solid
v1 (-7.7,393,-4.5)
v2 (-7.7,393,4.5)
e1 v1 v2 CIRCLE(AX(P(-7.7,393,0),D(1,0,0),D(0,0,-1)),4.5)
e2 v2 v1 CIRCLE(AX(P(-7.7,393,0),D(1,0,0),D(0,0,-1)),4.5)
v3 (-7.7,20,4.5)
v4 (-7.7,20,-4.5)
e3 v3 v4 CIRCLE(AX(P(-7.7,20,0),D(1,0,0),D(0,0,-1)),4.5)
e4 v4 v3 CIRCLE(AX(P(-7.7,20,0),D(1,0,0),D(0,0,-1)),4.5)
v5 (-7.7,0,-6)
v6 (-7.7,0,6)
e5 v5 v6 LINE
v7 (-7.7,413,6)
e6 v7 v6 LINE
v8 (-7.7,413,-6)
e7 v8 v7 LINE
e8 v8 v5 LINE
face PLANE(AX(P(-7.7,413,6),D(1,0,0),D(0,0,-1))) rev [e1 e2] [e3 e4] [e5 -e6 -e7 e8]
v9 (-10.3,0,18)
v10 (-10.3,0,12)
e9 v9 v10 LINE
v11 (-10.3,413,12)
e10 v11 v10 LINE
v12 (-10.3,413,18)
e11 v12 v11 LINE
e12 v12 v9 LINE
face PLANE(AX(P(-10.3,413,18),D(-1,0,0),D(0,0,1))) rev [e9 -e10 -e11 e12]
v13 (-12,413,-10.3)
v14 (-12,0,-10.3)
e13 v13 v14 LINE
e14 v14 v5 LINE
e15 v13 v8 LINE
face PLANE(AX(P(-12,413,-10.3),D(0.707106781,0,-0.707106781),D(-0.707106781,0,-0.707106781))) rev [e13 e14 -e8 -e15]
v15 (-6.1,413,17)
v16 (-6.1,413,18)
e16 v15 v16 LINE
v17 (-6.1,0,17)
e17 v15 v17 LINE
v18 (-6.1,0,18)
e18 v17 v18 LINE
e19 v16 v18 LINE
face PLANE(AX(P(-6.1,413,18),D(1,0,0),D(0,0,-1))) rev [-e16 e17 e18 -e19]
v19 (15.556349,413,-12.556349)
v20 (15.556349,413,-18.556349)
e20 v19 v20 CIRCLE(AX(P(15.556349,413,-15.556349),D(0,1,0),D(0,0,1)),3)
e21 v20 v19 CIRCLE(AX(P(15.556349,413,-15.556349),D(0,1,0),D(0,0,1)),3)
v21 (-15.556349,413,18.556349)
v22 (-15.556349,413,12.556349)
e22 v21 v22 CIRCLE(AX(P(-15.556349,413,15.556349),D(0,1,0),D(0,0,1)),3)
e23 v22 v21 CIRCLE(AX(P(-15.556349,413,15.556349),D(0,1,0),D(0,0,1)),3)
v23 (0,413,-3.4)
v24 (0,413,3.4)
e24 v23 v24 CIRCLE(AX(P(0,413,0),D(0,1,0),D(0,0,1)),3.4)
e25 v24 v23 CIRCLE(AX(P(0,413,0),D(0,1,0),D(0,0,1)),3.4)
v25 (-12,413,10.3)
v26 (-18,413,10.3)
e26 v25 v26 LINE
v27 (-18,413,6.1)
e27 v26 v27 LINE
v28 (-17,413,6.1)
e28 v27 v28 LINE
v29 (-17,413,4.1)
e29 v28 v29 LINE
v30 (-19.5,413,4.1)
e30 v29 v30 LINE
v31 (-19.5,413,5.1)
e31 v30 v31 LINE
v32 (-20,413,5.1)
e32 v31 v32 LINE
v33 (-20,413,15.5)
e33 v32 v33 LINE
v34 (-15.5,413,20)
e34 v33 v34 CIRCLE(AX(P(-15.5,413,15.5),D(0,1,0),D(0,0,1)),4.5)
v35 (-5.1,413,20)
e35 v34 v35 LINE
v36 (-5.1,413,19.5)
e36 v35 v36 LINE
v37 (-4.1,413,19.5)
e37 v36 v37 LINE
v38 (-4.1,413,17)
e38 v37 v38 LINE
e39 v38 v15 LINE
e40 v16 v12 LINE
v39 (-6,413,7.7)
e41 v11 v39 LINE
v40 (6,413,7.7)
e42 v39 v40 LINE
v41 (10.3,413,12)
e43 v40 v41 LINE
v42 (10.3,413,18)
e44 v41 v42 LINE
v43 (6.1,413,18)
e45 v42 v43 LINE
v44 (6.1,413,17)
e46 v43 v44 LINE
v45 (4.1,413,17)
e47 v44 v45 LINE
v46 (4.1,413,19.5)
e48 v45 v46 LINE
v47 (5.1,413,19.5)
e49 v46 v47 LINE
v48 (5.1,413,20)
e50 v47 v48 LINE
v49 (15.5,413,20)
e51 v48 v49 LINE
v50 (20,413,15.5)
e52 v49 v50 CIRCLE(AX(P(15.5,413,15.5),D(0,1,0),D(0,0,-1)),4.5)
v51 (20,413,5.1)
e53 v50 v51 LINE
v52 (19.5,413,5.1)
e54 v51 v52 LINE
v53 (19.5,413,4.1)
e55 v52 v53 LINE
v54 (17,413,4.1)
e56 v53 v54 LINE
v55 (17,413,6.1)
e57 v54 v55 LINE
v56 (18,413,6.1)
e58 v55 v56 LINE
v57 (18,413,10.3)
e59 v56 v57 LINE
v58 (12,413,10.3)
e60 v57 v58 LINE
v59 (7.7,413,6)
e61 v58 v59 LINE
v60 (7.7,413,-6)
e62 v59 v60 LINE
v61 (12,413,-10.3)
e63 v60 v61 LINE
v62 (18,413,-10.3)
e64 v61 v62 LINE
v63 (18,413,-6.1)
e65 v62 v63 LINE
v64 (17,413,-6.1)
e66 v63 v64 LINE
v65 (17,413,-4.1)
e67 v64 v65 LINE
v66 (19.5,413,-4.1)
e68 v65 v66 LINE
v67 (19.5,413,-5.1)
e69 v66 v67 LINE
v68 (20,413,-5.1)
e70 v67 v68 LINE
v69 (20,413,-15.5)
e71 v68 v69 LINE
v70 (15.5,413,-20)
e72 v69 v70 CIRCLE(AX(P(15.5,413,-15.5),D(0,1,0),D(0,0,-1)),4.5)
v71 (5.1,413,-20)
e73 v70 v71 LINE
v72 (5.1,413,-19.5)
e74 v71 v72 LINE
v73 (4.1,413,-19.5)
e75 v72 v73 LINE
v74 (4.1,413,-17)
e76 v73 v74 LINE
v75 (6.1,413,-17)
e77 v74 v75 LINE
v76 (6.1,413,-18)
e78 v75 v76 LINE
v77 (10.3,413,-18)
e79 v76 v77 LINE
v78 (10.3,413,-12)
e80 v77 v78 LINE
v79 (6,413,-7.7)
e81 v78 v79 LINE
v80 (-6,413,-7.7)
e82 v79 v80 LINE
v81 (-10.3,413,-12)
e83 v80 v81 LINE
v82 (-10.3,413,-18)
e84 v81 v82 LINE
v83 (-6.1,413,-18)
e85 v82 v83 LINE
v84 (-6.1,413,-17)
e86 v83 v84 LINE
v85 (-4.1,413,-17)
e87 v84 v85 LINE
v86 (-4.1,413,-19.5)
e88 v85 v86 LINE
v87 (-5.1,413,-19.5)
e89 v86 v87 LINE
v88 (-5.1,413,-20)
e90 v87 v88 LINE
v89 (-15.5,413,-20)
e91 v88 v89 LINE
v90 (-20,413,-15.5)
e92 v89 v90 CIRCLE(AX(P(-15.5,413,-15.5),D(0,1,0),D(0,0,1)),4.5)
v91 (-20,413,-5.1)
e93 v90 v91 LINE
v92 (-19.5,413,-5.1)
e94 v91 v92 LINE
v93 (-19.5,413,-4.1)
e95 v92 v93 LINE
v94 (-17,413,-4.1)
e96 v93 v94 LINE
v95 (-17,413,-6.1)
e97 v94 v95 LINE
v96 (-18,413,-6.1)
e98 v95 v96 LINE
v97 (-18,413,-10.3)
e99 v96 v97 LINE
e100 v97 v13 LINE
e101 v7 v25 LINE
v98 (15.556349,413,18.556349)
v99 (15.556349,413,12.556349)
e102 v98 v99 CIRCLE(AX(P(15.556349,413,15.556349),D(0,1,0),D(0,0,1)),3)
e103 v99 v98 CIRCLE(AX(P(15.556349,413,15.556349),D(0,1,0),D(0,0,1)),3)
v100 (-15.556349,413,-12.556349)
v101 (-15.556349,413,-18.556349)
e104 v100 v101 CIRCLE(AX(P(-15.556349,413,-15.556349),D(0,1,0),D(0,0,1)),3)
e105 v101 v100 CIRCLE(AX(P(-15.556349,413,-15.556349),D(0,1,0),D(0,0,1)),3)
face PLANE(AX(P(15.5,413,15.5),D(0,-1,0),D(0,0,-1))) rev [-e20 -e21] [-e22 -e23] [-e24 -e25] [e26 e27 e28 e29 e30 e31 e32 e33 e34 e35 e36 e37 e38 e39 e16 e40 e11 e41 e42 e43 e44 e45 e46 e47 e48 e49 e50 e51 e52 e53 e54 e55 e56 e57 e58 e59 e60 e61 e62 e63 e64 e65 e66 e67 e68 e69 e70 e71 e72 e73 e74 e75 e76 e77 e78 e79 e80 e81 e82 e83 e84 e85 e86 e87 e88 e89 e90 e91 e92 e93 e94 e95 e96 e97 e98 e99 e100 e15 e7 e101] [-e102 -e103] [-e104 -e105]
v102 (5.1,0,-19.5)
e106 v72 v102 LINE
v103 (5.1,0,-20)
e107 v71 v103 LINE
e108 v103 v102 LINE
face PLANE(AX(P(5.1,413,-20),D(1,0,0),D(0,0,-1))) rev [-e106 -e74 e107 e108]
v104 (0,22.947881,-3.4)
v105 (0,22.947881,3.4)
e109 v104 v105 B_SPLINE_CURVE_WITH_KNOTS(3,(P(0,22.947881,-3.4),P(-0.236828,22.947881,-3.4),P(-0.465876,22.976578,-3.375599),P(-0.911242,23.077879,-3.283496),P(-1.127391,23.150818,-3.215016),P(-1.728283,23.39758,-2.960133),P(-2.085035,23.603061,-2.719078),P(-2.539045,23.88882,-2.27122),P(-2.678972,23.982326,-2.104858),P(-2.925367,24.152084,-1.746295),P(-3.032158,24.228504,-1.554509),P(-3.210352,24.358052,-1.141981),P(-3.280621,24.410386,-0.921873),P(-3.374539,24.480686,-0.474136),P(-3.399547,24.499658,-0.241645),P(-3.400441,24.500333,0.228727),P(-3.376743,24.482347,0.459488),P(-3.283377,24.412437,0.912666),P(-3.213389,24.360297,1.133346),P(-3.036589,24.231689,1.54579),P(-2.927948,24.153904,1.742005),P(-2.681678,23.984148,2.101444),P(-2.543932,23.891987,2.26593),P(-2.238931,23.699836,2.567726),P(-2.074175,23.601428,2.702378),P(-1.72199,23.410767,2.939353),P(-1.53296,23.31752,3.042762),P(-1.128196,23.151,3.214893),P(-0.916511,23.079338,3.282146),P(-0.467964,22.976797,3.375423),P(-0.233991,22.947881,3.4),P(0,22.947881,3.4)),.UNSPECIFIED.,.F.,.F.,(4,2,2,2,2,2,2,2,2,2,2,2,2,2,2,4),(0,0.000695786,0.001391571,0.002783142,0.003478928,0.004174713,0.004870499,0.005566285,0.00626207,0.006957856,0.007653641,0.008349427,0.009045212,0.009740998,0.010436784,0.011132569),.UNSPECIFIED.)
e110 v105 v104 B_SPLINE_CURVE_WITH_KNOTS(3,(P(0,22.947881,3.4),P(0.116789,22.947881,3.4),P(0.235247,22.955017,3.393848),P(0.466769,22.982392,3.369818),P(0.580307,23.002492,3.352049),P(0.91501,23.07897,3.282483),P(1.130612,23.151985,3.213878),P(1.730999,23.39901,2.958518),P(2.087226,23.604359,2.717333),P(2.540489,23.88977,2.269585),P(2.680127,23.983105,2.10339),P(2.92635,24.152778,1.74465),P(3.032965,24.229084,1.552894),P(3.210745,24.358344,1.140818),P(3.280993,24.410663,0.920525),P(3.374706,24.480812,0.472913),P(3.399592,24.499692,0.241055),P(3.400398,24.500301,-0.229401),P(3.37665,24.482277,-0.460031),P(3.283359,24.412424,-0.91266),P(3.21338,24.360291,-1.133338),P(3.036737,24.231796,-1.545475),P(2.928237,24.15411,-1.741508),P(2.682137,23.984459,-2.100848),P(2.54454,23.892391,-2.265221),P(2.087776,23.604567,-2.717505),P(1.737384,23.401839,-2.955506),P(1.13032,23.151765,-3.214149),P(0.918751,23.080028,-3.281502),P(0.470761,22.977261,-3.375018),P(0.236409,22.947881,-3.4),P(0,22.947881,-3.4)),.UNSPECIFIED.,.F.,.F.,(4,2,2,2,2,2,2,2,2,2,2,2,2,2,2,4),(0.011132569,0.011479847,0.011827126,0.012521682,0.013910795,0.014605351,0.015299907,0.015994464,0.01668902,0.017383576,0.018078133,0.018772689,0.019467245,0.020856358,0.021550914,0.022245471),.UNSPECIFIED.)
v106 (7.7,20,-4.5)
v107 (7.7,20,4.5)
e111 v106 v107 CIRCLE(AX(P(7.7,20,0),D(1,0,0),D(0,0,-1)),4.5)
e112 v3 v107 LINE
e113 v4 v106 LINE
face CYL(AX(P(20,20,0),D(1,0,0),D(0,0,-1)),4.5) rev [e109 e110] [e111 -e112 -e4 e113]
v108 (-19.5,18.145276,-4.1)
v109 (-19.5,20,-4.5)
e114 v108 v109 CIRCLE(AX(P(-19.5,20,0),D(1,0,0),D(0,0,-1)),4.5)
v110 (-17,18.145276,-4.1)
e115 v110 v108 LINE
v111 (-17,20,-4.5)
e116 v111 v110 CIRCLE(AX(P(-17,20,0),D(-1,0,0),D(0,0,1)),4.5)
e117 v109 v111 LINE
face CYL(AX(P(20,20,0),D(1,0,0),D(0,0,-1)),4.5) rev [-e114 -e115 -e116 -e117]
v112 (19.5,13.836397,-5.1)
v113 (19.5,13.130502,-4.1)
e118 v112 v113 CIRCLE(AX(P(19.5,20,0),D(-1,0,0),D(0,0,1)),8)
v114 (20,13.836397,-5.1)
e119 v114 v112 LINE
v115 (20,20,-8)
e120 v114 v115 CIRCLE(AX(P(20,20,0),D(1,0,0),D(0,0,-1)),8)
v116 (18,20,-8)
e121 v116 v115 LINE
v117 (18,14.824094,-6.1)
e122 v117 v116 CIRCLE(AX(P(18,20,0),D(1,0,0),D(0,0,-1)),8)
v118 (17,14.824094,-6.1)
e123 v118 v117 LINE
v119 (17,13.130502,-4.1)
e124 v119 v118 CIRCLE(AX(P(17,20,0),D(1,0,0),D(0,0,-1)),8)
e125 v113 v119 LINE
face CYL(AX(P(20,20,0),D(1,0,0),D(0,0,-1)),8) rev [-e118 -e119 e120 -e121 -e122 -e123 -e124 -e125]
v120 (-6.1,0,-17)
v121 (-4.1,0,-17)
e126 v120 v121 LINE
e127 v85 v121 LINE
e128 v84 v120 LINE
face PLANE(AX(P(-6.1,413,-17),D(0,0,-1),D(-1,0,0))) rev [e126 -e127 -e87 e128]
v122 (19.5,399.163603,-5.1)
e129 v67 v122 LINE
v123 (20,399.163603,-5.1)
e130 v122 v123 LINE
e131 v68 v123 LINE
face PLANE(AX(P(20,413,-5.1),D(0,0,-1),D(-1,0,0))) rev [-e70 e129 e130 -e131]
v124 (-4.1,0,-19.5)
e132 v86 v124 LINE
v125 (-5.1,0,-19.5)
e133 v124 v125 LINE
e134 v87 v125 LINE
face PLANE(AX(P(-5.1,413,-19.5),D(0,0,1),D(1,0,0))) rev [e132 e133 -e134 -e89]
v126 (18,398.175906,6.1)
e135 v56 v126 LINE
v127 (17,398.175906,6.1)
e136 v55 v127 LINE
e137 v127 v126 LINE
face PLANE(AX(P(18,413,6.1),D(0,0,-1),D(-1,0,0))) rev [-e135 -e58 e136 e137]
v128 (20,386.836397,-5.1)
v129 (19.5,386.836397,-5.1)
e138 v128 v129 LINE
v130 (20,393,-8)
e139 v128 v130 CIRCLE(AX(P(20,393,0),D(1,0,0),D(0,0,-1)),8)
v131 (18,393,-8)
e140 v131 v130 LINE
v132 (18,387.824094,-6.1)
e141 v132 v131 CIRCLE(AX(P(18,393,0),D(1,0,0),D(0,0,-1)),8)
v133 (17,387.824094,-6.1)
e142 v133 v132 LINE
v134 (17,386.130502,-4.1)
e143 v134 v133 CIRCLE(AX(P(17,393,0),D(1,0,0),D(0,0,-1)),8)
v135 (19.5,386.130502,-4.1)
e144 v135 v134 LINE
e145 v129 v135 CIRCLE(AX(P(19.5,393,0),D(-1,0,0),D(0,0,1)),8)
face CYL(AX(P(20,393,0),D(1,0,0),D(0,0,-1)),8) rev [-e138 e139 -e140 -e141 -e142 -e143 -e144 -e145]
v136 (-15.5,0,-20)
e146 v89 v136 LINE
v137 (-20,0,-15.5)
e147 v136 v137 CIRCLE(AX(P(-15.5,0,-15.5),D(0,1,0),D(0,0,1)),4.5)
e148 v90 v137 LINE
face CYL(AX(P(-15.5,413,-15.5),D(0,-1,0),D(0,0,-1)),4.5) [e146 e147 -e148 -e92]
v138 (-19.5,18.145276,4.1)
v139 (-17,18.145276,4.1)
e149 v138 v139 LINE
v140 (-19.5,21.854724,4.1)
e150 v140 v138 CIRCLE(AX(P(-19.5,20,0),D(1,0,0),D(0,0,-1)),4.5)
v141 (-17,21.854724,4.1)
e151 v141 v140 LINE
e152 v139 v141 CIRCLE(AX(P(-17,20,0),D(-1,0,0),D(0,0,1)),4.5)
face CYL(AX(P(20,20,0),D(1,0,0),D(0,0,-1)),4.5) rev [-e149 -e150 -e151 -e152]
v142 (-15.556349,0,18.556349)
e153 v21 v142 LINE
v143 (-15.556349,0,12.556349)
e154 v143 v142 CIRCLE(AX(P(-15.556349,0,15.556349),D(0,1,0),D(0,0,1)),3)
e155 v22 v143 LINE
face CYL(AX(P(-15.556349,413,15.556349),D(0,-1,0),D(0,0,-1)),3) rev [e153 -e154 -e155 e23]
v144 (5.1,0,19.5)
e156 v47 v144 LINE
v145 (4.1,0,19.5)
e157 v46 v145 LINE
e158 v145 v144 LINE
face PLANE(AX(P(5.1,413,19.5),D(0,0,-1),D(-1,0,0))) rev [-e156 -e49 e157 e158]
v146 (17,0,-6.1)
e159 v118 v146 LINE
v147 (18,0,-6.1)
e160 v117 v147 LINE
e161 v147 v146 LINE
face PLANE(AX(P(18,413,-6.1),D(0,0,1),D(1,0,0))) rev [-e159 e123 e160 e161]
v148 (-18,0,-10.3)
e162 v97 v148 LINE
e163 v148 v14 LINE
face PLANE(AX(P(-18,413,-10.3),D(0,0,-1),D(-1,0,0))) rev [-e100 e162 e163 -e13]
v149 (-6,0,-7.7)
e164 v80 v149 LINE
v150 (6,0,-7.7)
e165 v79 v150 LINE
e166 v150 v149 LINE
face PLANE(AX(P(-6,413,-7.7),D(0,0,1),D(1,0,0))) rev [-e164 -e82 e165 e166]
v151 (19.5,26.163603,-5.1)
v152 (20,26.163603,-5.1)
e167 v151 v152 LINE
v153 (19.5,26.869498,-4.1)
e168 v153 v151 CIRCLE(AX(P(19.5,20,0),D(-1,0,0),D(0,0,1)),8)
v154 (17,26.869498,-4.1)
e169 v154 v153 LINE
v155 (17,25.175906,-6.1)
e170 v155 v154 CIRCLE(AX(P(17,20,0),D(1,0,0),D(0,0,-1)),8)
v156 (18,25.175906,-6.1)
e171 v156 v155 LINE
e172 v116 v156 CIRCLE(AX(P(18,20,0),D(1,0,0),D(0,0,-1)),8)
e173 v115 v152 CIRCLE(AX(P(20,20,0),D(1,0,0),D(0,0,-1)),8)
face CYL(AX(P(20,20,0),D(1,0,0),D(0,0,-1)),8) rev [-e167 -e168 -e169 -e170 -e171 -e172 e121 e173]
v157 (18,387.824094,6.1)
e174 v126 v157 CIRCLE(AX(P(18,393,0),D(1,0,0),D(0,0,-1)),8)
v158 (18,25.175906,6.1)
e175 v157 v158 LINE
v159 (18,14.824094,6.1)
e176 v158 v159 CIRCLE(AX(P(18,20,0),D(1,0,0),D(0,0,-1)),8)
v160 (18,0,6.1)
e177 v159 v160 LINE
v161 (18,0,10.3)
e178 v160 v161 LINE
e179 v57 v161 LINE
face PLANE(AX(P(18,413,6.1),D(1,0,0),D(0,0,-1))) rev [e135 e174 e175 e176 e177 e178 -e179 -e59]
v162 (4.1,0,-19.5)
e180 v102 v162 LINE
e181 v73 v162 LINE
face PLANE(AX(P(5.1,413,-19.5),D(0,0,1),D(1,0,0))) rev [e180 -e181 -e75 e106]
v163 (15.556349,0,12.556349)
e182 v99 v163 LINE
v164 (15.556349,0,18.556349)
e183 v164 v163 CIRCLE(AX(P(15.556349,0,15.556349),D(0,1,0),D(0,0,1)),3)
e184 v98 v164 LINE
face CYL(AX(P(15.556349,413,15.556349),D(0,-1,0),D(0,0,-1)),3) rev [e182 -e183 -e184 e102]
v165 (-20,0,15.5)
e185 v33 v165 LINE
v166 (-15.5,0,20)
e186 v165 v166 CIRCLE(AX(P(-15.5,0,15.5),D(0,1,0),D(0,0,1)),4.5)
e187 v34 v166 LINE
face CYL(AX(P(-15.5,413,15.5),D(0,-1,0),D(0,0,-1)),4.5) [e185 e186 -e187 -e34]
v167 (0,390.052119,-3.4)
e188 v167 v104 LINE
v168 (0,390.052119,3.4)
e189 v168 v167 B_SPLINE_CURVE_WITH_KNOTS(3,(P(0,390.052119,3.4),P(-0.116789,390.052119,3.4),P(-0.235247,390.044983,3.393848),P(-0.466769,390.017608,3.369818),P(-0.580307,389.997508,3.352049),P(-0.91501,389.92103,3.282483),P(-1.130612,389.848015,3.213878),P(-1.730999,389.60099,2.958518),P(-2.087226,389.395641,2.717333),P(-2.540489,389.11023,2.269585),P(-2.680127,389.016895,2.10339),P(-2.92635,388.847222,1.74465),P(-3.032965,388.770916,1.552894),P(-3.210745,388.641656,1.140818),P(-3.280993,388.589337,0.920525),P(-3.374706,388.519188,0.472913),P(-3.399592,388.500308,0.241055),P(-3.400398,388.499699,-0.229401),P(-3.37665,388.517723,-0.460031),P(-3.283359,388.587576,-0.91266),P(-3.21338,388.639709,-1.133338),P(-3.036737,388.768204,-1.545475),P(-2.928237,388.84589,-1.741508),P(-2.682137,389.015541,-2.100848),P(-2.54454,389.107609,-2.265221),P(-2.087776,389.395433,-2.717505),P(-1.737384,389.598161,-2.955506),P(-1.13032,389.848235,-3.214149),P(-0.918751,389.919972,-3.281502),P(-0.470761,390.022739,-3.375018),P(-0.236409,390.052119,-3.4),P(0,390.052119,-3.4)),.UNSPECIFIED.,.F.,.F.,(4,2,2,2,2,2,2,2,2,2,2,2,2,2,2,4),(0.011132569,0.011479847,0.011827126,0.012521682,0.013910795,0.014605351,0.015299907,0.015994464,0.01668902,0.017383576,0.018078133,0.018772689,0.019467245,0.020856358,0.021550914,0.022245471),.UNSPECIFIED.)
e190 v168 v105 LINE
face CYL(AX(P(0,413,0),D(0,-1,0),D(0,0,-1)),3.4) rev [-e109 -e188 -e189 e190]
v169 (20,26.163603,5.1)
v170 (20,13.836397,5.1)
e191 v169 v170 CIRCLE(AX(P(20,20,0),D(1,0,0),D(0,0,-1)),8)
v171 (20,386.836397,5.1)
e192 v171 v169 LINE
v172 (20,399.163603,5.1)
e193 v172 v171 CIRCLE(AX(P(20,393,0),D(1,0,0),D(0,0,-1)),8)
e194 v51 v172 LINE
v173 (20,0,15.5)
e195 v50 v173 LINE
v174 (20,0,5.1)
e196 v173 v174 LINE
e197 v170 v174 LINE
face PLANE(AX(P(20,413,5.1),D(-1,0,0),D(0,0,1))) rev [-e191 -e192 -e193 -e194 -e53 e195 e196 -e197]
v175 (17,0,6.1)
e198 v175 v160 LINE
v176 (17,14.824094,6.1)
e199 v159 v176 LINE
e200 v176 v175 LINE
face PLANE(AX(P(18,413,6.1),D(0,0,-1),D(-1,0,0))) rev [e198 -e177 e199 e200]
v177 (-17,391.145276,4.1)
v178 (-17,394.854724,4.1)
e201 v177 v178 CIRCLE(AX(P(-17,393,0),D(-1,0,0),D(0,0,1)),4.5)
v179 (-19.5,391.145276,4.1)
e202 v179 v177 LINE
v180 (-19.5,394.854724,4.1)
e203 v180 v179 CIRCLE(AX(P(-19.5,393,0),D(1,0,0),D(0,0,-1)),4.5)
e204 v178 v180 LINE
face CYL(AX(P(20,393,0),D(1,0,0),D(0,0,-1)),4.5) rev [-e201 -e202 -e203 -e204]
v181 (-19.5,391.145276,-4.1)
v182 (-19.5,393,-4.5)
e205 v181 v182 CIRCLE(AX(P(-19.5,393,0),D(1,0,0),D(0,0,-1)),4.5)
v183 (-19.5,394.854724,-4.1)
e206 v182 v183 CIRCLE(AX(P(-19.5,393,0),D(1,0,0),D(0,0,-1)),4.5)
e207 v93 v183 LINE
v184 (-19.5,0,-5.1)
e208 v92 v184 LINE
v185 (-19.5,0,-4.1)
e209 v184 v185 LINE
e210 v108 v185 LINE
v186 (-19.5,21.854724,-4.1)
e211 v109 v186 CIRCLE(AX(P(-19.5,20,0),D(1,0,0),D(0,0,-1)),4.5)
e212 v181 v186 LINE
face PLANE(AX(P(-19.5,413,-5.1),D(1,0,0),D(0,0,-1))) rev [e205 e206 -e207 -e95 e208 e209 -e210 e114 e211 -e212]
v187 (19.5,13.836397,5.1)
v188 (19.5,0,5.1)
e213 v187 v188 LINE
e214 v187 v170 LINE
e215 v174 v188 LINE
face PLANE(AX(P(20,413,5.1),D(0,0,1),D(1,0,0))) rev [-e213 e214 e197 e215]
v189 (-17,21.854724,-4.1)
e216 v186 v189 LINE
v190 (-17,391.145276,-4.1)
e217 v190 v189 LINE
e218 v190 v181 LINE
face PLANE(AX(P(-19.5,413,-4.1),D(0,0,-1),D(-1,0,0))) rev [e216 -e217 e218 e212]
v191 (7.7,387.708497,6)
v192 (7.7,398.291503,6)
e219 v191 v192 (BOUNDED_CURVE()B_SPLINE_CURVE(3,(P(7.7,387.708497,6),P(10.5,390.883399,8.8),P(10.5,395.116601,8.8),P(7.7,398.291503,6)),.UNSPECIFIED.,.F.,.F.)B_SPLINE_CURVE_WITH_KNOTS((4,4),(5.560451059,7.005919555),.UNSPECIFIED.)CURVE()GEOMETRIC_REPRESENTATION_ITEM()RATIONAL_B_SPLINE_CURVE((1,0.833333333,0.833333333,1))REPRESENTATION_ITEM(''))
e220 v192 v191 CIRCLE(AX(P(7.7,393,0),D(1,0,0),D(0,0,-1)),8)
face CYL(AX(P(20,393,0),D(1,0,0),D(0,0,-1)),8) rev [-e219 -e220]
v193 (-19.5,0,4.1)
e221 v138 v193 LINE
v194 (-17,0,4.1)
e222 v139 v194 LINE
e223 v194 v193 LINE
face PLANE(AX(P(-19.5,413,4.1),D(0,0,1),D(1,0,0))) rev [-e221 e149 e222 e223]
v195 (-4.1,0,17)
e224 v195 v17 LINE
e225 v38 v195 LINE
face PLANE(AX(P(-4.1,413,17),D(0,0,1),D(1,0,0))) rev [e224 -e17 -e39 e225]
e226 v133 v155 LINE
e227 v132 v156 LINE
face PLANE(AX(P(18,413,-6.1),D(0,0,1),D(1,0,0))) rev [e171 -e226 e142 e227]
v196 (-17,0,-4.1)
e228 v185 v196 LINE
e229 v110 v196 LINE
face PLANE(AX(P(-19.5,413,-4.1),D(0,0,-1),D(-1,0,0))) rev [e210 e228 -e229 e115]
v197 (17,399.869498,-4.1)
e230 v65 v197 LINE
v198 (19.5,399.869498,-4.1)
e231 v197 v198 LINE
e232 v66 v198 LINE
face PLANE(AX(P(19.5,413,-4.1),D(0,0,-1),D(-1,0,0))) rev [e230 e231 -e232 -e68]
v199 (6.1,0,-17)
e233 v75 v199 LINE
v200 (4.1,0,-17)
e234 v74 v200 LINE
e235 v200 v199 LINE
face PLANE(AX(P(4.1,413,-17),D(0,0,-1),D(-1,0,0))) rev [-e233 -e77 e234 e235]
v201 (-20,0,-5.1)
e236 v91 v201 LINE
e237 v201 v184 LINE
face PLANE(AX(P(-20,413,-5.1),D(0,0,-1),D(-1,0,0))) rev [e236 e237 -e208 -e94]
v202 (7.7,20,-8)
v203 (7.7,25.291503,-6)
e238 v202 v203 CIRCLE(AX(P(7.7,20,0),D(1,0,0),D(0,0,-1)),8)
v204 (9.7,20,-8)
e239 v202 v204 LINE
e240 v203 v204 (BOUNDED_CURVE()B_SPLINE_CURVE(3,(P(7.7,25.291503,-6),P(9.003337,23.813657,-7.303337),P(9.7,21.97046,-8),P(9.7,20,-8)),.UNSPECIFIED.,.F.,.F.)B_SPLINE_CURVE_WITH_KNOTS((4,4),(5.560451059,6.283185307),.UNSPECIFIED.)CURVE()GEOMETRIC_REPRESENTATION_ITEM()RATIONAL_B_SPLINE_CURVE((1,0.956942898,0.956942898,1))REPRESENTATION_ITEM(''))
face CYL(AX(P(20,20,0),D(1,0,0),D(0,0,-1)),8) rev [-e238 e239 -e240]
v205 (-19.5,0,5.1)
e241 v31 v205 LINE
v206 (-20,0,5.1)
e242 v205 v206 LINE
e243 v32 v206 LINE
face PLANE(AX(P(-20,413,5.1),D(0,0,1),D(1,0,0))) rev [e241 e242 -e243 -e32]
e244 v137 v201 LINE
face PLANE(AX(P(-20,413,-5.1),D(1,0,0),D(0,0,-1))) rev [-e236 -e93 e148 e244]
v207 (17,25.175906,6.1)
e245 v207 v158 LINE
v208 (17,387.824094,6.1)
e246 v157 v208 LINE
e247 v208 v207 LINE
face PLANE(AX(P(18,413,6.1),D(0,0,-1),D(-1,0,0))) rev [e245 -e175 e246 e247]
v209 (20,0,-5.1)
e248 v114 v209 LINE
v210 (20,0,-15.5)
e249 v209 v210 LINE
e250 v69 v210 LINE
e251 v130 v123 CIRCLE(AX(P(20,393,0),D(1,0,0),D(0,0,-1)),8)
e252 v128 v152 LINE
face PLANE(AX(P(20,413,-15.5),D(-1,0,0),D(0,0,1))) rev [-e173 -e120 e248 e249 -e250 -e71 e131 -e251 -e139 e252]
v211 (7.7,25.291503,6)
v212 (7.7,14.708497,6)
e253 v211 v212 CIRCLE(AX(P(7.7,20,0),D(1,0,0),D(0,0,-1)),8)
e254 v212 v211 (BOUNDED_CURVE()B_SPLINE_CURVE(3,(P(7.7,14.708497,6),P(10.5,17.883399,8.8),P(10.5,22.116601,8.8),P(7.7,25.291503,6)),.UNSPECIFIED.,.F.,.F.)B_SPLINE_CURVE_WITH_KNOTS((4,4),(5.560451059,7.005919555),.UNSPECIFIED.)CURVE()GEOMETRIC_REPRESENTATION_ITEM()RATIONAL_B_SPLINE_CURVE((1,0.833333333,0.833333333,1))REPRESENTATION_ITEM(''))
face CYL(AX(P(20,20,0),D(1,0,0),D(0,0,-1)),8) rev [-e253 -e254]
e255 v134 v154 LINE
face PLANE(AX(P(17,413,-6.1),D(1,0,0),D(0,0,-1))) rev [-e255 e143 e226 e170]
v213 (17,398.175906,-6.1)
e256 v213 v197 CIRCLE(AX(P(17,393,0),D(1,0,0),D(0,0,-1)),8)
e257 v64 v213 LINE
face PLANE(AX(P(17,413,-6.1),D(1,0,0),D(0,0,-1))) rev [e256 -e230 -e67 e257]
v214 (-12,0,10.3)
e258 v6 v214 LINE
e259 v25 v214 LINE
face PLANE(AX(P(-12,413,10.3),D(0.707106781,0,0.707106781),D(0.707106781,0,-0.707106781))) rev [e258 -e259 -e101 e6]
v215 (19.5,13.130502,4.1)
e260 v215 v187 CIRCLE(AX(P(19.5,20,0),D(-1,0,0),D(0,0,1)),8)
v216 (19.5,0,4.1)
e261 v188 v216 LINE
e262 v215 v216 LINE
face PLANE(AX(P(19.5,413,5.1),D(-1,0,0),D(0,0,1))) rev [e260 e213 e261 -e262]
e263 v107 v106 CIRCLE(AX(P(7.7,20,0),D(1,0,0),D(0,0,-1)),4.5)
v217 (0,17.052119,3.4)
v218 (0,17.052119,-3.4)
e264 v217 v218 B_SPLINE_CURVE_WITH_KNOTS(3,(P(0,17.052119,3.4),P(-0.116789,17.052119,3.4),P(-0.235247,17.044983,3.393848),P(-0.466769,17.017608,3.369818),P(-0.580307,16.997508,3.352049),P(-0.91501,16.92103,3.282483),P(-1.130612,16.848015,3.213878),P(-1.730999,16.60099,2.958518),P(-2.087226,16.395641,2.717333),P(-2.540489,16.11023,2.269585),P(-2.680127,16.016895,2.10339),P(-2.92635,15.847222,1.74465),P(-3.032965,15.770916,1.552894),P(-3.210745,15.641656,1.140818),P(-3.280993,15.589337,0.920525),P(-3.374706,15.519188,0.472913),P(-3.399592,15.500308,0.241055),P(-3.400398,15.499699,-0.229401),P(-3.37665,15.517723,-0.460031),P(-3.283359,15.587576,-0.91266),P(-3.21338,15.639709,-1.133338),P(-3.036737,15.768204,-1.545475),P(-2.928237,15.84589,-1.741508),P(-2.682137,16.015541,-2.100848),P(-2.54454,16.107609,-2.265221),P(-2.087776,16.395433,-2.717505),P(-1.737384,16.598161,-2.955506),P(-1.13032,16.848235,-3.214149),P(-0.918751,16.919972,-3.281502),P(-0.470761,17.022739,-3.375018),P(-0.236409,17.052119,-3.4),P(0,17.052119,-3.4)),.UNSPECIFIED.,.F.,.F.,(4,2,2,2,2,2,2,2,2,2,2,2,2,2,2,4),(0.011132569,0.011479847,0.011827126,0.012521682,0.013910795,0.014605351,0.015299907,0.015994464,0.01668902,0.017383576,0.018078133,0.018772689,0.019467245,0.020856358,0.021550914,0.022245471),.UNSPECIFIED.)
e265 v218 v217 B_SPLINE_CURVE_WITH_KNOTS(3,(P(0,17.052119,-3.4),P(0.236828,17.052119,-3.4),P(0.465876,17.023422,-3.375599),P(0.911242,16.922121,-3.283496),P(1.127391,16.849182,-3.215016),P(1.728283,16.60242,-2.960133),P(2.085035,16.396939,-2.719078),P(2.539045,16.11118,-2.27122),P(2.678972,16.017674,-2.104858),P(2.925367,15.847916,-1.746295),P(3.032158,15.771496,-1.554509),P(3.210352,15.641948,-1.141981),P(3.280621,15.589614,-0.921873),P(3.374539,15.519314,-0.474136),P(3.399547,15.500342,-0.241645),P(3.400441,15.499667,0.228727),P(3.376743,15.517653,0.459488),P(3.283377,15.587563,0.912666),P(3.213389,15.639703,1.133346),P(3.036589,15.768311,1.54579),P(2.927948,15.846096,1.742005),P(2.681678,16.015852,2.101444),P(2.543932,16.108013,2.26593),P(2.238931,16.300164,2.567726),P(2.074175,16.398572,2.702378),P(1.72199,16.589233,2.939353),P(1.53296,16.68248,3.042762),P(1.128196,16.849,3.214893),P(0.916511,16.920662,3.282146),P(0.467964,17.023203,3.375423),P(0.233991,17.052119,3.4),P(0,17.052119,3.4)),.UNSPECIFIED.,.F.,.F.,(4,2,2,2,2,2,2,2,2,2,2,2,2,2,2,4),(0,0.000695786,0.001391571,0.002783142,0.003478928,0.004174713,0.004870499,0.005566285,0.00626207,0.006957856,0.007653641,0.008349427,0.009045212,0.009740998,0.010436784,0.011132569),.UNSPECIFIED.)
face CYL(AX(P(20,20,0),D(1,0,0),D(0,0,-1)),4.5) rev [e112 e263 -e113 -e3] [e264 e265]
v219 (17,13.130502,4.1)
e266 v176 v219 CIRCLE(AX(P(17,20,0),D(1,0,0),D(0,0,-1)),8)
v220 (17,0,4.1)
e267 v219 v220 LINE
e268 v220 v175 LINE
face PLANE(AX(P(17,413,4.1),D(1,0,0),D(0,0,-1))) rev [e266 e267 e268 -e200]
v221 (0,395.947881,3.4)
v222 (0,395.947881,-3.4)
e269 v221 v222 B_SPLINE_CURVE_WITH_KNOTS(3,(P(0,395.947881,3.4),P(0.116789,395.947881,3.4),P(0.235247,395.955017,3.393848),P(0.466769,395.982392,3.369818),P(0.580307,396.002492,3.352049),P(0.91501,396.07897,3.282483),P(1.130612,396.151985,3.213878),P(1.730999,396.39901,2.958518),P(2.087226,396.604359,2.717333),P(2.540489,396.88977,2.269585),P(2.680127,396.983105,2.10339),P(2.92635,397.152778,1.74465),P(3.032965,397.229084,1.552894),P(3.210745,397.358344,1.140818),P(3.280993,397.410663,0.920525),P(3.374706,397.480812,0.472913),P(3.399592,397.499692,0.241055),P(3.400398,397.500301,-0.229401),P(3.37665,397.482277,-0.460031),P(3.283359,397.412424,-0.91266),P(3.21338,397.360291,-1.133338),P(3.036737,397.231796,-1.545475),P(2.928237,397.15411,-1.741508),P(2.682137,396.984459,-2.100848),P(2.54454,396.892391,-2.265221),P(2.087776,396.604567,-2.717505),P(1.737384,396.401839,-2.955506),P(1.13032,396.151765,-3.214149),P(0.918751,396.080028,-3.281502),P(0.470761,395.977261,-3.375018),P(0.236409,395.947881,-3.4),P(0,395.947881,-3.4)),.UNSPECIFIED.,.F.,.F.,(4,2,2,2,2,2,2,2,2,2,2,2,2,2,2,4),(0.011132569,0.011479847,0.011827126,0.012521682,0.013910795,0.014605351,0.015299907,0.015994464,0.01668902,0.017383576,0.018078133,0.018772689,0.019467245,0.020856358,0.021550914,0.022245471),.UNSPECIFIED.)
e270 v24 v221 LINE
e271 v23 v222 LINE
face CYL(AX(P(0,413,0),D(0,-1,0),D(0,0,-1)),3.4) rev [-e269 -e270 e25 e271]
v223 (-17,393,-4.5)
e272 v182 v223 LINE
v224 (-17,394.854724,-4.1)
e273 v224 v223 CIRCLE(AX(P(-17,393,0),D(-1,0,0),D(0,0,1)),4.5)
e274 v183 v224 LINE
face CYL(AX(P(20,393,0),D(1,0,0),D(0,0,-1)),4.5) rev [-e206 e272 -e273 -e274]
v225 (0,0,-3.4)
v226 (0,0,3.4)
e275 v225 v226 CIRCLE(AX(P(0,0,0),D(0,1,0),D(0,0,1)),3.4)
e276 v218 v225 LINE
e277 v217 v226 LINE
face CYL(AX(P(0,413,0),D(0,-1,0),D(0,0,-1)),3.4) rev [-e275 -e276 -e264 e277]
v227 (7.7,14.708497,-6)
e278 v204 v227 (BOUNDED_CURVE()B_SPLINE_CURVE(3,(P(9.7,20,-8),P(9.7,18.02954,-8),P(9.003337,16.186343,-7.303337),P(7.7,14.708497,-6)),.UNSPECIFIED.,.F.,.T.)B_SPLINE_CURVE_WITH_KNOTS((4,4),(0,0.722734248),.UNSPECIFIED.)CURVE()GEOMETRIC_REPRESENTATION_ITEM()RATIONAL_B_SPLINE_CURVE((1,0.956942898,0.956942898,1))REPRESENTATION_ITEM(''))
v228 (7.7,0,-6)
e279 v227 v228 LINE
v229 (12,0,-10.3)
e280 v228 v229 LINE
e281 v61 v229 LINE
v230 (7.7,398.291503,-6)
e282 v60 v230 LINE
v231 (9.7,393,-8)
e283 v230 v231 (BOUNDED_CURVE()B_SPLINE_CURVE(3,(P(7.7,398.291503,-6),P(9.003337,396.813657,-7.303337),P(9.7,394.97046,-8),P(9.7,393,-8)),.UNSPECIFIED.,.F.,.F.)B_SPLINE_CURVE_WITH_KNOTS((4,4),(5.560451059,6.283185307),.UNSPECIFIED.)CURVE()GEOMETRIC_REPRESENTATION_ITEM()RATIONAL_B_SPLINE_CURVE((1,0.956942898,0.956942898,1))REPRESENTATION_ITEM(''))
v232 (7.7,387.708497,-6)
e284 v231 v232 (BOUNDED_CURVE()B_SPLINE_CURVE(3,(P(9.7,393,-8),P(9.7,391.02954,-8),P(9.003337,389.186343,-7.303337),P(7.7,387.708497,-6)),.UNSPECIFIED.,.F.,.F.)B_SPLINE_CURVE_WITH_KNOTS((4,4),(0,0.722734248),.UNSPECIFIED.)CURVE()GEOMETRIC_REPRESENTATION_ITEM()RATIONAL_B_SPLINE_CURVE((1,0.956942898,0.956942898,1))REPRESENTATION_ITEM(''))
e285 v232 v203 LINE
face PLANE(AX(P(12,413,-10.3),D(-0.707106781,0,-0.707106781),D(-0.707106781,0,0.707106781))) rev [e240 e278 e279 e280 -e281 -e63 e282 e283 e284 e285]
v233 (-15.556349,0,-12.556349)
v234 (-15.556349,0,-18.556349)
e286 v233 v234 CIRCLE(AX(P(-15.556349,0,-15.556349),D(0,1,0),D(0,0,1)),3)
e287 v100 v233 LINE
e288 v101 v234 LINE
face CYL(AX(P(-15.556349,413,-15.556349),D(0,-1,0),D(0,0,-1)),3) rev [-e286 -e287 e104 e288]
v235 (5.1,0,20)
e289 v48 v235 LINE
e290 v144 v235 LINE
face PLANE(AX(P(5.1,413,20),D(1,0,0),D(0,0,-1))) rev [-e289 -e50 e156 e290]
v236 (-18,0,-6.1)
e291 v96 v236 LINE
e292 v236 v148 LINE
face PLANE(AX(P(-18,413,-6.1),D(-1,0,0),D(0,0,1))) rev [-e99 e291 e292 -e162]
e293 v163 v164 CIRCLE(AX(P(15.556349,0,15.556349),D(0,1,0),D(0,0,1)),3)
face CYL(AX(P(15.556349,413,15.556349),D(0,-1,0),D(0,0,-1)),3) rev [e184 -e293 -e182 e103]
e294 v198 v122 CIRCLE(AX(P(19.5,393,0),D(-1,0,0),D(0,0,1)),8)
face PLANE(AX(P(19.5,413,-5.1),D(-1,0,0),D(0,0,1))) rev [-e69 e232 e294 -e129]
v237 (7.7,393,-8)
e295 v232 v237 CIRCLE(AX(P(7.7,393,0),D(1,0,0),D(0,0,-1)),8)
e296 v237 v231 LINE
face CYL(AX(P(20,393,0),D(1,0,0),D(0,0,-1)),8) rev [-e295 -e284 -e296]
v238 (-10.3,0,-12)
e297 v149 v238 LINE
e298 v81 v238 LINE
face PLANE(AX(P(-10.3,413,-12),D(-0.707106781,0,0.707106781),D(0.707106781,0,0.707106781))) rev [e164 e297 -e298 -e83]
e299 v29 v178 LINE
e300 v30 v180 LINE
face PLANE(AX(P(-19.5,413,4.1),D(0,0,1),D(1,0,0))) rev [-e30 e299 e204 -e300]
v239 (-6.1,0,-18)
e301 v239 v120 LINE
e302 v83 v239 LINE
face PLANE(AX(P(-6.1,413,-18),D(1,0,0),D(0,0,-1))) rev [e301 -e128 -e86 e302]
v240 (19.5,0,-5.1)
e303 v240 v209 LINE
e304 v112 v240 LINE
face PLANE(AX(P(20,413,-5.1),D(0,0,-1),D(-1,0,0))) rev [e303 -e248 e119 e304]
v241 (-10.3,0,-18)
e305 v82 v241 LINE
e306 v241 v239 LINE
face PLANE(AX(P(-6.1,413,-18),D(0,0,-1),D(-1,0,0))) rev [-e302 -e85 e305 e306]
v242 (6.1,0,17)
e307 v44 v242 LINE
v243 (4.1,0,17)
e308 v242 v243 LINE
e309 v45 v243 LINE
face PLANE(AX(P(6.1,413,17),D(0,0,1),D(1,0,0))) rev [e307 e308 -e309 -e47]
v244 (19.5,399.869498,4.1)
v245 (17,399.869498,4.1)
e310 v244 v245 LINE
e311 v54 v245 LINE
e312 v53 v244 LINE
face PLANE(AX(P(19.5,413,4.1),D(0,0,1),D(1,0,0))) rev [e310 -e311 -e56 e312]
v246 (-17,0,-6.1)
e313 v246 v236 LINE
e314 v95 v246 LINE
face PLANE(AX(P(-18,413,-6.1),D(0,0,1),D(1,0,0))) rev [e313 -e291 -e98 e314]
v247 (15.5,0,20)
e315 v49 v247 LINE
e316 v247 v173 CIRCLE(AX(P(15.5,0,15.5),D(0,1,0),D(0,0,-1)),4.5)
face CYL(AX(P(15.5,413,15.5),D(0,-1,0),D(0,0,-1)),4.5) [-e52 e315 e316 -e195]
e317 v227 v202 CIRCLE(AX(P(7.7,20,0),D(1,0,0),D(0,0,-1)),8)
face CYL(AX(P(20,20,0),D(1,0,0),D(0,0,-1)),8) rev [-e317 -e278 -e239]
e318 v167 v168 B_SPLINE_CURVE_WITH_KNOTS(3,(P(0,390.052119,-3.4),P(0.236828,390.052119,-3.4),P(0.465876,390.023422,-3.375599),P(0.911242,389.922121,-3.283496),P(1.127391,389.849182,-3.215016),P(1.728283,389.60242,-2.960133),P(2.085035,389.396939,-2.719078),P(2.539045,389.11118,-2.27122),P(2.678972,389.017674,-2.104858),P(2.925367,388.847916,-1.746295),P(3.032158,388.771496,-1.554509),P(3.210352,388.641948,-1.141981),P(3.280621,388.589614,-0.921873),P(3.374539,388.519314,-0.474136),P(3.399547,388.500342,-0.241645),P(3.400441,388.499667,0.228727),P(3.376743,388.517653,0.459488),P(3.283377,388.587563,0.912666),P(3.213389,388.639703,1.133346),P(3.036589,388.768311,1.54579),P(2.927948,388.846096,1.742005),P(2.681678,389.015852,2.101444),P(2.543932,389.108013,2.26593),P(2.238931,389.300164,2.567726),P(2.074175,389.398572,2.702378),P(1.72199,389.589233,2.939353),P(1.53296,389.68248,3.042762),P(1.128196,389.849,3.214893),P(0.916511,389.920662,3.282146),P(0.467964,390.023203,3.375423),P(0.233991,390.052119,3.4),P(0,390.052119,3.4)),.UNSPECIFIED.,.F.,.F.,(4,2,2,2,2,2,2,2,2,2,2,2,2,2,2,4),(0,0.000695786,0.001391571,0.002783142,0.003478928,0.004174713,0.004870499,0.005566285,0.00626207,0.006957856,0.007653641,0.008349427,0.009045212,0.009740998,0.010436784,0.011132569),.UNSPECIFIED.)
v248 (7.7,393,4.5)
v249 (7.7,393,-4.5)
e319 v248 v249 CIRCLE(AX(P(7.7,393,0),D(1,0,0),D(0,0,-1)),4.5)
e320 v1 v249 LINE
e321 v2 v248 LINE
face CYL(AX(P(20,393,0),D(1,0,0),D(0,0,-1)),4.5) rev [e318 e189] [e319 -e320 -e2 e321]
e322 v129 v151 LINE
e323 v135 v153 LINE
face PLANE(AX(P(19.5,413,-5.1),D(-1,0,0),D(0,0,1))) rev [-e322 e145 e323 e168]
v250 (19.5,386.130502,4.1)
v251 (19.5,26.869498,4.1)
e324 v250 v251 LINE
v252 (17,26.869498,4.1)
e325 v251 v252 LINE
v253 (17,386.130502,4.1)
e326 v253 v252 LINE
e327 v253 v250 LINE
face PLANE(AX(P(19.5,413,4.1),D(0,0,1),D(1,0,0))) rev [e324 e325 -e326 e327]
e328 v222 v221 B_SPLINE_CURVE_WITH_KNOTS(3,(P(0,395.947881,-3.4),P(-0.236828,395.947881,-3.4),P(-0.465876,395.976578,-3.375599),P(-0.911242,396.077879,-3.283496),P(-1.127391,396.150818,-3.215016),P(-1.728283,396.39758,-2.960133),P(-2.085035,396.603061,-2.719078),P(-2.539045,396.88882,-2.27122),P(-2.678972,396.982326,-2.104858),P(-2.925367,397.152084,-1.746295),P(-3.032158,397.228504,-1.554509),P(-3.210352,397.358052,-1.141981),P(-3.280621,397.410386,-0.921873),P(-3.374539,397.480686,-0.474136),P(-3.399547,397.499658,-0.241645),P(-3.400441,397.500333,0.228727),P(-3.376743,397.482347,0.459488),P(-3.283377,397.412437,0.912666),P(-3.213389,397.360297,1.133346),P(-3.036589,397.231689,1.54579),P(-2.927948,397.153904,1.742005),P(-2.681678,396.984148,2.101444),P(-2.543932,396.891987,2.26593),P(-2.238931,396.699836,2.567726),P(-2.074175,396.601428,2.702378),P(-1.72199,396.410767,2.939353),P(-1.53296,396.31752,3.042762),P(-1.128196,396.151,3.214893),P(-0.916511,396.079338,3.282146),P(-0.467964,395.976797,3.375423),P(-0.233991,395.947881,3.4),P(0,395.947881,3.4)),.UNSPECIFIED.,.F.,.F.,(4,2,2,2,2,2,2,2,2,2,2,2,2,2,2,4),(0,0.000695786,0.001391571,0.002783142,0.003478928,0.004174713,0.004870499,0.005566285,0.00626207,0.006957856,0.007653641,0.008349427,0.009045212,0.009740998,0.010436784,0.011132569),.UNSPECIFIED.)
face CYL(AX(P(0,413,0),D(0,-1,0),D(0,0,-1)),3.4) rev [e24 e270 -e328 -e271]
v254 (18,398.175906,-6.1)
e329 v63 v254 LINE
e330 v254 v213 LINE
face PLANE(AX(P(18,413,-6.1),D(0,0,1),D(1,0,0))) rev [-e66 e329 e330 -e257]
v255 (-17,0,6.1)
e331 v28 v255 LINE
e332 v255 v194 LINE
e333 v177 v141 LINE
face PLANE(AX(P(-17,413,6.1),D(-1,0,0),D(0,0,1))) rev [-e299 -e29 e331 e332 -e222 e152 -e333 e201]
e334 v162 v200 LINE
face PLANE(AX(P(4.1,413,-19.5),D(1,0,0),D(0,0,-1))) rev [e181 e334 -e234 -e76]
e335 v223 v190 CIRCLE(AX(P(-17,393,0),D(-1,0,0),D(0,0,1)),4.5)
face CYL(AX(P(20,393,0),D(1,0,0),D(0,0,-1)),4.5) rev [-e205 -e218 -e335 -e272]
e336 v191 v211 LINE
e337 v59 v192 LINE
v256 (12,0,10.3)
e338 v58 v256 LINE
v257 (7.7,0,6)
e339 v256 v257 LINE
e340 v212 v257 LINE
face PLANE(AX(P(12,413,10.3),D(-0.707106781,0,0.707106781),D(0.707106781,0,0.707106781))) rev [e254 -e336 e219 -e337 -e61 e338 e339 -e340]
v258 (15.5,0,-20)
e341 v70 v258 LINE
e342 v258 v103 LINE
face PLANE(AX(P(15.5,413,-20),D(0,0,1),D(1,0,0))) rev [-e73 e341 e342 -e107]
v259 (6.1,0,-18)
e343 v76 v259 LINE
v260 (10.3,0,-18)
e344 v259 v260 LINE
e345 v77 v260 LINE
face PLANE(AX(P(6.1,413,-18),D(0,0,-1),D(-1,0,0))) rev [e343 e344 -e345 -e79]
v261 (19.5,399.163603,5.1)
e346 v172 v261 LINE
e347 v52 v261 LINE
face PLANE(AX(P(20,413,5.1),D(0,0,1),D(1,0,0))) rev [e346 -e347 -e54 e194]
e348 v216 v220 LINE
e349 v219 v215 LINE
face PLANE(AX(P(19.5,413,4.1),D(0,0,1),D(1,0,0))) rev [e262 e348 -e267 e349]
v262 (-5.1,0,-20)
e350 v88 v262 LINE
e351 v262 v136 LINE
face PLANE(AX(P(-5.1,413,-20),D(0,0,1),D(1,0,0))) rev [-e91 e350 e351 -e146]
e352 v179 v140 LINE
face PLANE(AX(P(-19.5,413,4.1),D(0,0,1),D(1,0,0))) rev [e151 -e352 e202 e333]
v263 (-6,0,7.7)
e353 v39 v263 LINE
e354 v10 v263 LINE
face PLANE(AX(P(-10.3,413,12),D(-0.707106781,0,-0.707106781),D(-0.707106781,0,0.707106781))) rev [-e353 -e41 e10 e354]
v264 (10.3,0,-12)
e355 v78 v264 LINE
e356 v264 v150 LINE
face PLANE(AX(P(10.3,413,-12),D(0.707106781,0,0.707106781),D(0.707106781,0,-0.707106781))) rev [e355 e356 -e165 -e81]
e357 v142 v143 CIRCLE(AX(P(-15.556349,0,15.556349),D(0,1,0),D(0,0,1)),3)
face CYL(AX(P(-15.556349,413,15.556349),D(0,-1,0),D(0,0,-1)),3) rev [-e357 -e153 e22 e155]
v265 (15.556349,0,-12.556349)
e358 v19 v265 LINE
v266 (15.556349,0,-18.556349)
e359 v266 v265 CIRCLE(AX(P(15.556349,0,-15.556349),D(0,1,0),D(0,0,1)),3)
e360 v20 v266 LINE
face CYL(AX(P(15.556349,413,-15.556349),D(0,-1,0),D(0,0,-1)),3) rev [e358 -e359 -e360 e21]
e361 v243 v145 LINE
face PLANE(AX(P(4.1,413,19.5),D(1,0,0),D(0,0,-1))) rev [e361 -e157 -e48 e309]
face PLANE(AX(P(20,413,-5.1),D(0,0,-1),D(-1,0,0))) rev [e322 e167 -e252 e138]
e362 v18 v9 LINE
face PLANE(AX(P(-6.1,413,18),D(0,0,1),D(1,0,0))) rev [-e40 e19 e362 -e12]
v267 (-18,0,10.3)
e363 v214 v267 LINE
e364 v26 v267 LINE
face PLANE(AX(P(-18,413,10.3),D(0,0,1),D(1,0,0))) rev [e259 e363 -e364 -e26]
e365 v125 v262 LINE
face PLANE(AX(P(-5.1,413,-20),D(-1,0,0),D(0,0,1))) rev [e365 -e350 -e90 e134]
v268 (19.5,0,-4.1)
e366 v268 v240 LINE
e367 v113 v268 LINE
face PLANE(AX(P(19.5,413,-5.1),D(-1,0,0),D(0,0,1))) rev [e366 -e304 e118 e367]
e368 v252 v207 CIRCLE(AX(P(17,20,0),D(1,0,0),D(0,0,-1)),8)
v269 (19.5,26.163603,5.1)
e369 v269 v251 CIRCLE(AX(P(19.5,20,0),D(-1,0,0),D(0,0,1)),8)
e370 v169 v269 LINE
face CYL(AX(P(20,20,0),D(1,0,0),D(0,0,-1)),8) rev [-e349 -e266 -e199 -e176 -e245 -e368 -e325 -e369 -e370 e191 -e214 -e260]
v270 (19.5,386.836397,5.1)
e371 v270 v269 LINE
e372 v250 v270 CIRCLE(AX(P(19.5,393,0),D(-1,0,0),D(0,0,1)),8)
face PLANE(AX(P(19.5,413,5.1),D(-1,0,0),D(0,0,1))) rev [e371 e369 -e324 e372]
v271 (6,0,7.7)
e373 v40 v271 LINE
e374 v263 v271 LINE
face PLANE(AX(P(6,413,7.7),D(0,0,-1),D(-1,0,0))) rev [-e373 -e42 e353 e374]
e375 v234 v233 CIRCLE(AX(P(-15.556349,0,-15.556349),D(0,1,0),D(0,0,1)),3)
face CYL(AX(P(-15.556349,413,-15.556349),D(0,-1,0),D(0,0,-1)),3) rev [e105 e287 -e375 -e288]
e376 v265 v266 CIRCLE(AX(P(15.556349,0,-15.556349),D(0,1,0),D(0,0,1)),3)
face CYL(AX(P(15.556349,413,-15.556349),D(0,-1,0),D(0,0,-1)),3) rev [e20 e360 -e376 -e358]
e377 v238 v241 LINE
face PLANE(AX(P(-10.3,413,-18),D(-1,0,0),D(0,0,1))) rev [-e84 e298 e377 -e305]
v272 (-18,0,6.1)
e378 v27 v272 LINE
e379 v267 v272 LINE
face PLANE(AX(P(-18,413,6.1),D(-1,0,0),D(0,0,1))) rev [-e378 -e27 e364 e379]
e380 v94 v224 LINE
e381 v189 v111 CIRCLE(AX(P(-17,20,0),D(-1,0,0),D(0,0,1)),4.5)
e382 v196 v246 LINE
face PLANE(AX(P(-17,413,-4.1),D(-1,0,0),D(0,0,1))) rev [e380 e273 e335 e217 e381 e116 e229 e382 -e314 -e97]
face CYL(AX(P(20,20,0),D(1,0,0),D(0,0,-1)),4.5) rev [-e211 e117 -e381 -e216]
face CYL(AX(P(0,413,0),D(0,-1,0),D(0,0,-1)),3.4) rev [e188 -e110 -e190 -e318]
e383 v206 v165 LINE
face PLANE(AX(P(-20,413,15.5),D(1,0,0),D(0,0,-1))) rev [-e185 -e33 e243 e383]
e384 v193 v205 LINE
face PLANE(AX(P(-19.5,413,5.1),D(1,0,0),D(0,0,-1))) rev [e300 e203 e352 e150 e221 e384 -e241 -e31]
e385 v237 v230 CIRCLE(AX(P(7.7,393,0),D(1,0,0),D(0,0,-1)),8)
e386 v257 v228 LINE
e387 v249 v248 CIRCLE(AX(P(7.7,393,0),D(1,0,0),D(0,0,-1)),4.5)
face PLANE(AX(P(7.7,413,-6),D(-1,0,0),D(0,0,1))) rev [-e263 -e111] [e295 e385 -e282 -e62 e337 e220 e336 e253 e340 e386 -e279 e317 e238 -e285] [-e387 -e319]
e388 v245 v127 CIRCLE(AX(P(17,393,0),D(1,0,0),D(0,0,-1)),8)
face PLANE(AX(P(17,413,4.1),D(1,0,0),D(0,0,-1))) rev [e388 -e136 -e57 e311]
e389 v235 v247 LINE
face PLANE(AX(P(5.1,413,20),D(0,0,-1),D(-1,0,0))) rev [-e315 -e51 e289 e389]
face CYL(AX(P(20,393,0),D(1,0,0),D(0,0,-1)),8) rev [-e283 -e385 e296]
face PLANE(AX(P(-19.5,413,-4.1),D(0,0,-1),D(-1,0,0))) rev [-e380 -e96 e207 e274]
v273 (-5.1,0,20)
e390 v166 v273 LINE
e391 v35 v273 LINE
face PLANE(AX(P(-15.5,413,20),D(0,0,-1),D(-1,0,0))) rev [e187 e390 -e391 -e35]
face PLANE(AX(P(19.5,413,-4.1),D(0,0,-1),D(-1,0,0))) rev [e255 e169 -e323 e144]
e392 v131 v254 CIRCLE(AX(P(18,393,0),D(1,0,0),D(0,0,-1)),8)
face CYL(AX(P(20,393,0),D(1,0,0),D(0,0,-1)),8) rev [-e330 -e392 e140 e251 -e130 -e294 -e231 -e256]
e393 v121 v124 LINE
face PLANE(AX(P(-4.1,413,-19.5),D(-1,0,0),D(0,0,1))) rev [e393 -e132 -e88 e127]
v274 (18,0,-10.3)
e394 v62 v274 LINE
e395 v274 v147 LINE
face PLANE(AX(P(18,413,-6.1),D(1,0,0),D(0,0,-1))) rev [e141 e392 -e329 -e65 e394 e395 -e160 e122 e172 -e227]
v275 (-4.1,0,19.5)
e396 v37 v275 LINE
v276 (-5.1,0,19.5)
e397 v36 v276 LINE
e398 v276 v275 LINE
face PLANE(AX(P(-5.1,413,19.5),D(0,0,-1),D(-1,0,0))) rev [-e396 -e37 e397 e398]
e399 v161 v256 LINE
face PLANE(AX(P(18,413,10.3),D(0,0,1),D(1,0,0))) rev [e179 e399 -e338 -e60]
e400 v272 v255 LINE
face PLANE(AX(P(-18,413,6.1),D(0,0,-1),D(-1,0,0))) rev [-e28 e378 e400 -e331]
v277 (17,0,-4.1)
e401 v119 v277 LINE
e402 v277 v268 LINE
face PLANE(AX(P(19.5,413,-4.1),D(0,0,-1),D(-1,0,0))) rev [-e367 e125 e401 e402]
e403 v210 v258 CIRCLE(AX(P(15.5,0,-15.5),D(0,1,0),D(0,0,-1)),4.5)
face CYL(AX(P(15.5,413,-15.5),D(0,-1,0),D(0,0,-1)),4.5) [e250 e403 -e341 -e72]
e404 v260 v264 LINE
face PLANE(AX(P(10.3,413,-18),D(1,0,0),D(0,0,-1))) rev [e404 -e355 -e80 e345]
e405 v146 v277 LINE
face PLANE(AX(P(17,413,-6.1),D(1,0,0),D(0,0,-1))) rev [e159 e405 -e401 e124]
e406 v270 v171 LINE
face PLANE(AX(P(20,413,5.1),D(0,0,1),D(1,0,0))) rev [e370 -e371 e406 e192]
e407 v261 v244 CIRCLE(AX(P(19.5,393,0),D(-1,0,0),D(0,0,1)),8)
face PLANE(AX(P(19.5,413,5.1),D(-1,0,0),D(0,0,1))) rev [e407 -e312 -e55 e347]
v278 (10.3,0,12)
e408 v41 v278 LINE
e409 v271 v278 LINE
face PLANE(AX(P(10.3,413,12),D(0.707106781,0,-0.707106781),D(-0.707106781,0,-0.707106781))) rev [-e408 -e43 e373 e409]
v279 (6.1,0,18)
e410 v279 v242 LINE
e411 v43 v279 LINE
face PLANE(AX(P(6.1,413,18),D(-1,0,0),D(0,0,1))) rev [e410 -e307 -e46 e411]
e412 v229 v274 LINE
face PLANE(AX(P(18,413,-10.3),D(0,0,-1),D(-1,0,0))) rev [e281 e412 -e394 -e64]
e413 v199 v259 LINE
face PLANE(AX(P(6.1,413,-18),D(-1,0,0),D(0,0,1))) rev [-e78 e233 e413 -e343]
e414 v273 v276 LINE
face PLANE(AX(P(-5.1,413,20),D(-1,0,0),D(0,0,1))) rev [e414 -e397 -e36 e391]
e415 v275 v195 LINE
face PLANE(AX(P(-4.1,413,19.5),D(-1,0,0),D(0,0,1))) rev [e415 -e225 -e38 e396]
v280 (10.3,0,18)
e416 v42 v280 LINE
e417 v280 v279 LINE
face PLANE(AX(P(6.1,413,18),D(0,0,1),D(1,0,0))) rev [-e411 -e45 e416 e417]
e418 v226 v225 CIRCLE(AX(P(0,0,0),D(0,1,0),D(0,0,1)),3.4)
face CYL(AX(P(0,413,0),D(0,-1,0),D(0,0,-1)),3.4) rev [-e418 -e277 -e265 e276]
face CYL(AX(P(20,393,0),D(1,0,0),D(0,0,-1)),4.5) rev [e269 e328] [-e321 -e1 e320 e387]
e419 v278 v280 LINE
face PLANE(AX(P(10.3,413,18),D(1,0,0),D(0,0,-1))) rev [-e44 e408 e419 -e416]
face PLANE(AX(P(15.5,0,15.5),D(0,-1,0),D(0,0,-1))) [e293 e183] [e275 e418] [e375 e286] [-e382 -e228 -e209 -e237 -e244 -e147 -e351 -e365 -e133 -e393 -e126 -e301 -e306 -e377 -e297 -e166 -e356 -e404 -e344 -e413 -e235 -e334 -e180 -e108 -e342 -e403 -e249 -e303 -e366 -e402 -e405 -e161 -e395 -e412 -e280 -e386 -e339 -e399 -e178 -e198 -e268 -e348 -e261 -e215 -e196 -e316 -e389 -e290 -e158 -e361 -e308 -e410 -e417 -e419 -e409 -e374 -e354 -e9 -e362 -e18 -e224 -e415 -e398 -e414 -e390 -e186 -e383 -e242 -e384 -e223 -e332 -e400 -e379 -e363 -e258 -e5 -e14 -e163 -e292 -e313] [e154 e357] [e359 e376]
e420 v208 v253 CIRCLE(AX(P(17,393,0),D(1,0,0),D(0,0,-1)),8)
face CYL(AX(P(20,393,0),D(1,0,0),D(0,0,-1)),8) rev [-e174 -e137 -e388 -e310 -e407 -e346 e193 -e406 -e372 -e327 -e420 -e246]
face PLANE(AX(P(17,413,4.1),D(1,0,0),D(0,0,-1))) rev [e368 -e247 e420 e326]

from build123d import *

# Parameters (mm, degrees)
SKETCH16_R                   = 3.4
SKETCH16_R_2                 = 3
MEMBER_1_DEPTH               = 413
HOLE_WIZARD_M8_1_D           = 9
HOLE_WIZARD_M8_1_CBORE_D     = 16
HOLE_WIZARD_M8_1_CBORE_DEPTH = 12.3


with BuildPart() as part:
    # Sketch16 → Member 1 (new body)
    with BuildSketch(Plane(origin=(0, 0, 0), x_dir=(-1, 0, 0), z_dir=(0, 1, 0))):
        with BuildLine():
            Line((-5.1, 20), (-5.1, 19.5))
            Line((-5.1, 19.5), (-4.1, 19.5))
            Line((-4.1, 19.5), (-4.1, 17))
            Line((-4.1, 17), (-6.1, 17))
            Line((-6.1, 17), (-6.1, 18))
            Line((-6.1, 18), (-10.3, 18))
            Line((-10.3, 18), (-10.3, 12))
            Line((-10.3, 12), (-6, 7.7))
            Line((-6, 7.7), (6, 7.7))
            Line((6, 7.7), (10.3, 12))
            Line((10.3, 12), (10.3, 18))
            Line((10.3, 18), (6.1, 18))
            Line((6.1, 18), (6.1, 17))
            Line((6.1, 17), (4.1, 17))
            Line((4.1, 17), (4.1, 19.5))
            Line((4.1, 19.5), (5.1, 19.5))
            Line((5.1, 19.5), (5.1, 20))
            Line((5.1, 20), (15.5, 20))
            ThreePointArc((15.5, 20), (18.681980515, 18.681980515), (20, 15.5))
            Line((20, 15.5), (20, 5.1))
            Line((20, 5.1), (19.5, 5.1))
            Line((19.5, 5.1), (19.5, 4.1))
            Line((19.5, 4.1), (17, 4.1))
            Line((17, 4.1), (17, 6.1))
            Line((17, 6.1), (18, 6.1))
            Line((18, 6.1), (18, 10.3))
            Line((18, 10.3), (12, 10.3))
            Line((12, 10.3), (7.7, 6))
            Line((7.7, 6), (7.7, -6))
            Line((7.7, -6), (12, -10.3))
            Line((12, -10.3), (18, -10.3))
            Line((18, -10.3), (18, -6.1))
            Line((18, -6.1), (17, -6.1))
            Line((17, -6.1), (17, -4.1))
            Line((17, -4.1), (19.5, -4.1))
            Line((19.5, -4.1), (19.5, -5.1))
            Line((19.5, -5.1), (20, -5.1))
            Line((20, -5.1), (20, -15.5))
            ThreePointArc((20, -15.5), (18.681980515, -18.681980515), (15.5, -20))
            Line((15.5, -20), (5.1, -20))
            Line((5.1, -20), (5.1, -19.5))
            Line((5.1, -19.5), (4.1, -19.5))
            Line((4.1, -19.5), (4.1, -17))
            Line((4.1, -17), (6.1, -17))
            Line((6.1, -17), (6.1, -18))
            Line((6.1, -18), (10.3, -18))
            Line((10.3, -18), (10.3, -12))
            Line((10.3, -12), (6, -7.7))
            Line((6, -7.7), (-6, -7.7))
            Line((-6, -7.7), (-10.3, -12))
            Line((-10.3, -12), (-10.3, -18))
            Line((-10.3, -18), (-6.1, -18))
            Line((-6.1, -18), (-6.1, -17))
            Line((-6.1, -17), (-4.1, -17))
            Line((-4.1, -17), (-4.1, -19.5))
            Line((-4.1, -19.5), (-5.1, -19.5))
            Line((-5.1, -19.5), (-5.1, -20))
            Line((-5.1, -20), (-15.5, -20))
            ThreePointArc((-15.5, -20), (-18.681980515, -18.681980515), (-20, -15.5))
            Line((-20, -15.5), (-20, -5.1))
            Line((-20, -5.1), (-19.5, -5.1))
            Line((-19.5, -5.1), (-19.5, -4.1))
            Line((-19.5, -4.1), (-17, -4.1))
            Line((-17, -4.1), (-17, -6.1))
            Line((-17, -6.1), (-18, -6.1))
            Line((-18, -6.1), (-18, -10.3))
            Line((-18, -10.3), (-12, -10.3))
            Line((-12, -10.3), (-7.7, -6))
            Line((-7.7, -6), (-7.7, 6))
            Line((-7.7, 6), (-12, 10.3))
            Line((-12, 10.3), (-18, 10.3))
            Line((-18, 10.3), (-18, 6.1))
            Line((-18, 6.1), (-17, 6.1))
            Line((-17, 6.1), (-17, 4.1))
            Line((-17, 4.1), (-19.5, 4.1))
            Line((-19.5, 4.1), (-19.5, 5.1))
            Line((-19.5, 5.1), (-20, 5.1))
            Line((-20, 5.1), (-20, 15.5))
            ThreePointArc((-20, 15.5), (-18.681980515, 18.681980515), (-15.5, 20))
            Line((-15.5, 20), (-5.1, 20))
        make_face()
        Circle(SKETCH16_R, mode=Mode.SUBTRACT)
        with Locations((-15.556349186, 15.556349186)):
            Circle(SKETCH16_R_2, mode=Mode.SUBTRACT)
        with Locations((15.556349186, 15.556349186)):
            Circle(SKETCH16_R_2, mode=Mode.SUBTRACT)
        with Locations((15.556349186, -15.556349186)):
            Circle(SKETCH16_R_2, mode=Mode.SUBTRACT)
        with Locations((-15.556349186, -15.556349186)):
            Circle(SKETCH16_R_2, mode=Mode.SUBTRACT)
    extrude(amount=MEMBER_1_DEPTH)

    # M8 六角凹头螺钉的柱形沉头孔1 (through all)
    with Locations(Plane(origin=(20, 0, 0), x_dir=(0, 0, -1), z_dir=(1, 0, 0))):
        with Locations((0, 20), (0, 393)):
            CounterBoreHole(HOLE_WIZARD_M8_1_D / 2, HOLE_WIZARD_M8_1_CBORE_D / 2, HOLE_WIZARD_M8_1_CBORE_DEPTH)


solid = part.part
